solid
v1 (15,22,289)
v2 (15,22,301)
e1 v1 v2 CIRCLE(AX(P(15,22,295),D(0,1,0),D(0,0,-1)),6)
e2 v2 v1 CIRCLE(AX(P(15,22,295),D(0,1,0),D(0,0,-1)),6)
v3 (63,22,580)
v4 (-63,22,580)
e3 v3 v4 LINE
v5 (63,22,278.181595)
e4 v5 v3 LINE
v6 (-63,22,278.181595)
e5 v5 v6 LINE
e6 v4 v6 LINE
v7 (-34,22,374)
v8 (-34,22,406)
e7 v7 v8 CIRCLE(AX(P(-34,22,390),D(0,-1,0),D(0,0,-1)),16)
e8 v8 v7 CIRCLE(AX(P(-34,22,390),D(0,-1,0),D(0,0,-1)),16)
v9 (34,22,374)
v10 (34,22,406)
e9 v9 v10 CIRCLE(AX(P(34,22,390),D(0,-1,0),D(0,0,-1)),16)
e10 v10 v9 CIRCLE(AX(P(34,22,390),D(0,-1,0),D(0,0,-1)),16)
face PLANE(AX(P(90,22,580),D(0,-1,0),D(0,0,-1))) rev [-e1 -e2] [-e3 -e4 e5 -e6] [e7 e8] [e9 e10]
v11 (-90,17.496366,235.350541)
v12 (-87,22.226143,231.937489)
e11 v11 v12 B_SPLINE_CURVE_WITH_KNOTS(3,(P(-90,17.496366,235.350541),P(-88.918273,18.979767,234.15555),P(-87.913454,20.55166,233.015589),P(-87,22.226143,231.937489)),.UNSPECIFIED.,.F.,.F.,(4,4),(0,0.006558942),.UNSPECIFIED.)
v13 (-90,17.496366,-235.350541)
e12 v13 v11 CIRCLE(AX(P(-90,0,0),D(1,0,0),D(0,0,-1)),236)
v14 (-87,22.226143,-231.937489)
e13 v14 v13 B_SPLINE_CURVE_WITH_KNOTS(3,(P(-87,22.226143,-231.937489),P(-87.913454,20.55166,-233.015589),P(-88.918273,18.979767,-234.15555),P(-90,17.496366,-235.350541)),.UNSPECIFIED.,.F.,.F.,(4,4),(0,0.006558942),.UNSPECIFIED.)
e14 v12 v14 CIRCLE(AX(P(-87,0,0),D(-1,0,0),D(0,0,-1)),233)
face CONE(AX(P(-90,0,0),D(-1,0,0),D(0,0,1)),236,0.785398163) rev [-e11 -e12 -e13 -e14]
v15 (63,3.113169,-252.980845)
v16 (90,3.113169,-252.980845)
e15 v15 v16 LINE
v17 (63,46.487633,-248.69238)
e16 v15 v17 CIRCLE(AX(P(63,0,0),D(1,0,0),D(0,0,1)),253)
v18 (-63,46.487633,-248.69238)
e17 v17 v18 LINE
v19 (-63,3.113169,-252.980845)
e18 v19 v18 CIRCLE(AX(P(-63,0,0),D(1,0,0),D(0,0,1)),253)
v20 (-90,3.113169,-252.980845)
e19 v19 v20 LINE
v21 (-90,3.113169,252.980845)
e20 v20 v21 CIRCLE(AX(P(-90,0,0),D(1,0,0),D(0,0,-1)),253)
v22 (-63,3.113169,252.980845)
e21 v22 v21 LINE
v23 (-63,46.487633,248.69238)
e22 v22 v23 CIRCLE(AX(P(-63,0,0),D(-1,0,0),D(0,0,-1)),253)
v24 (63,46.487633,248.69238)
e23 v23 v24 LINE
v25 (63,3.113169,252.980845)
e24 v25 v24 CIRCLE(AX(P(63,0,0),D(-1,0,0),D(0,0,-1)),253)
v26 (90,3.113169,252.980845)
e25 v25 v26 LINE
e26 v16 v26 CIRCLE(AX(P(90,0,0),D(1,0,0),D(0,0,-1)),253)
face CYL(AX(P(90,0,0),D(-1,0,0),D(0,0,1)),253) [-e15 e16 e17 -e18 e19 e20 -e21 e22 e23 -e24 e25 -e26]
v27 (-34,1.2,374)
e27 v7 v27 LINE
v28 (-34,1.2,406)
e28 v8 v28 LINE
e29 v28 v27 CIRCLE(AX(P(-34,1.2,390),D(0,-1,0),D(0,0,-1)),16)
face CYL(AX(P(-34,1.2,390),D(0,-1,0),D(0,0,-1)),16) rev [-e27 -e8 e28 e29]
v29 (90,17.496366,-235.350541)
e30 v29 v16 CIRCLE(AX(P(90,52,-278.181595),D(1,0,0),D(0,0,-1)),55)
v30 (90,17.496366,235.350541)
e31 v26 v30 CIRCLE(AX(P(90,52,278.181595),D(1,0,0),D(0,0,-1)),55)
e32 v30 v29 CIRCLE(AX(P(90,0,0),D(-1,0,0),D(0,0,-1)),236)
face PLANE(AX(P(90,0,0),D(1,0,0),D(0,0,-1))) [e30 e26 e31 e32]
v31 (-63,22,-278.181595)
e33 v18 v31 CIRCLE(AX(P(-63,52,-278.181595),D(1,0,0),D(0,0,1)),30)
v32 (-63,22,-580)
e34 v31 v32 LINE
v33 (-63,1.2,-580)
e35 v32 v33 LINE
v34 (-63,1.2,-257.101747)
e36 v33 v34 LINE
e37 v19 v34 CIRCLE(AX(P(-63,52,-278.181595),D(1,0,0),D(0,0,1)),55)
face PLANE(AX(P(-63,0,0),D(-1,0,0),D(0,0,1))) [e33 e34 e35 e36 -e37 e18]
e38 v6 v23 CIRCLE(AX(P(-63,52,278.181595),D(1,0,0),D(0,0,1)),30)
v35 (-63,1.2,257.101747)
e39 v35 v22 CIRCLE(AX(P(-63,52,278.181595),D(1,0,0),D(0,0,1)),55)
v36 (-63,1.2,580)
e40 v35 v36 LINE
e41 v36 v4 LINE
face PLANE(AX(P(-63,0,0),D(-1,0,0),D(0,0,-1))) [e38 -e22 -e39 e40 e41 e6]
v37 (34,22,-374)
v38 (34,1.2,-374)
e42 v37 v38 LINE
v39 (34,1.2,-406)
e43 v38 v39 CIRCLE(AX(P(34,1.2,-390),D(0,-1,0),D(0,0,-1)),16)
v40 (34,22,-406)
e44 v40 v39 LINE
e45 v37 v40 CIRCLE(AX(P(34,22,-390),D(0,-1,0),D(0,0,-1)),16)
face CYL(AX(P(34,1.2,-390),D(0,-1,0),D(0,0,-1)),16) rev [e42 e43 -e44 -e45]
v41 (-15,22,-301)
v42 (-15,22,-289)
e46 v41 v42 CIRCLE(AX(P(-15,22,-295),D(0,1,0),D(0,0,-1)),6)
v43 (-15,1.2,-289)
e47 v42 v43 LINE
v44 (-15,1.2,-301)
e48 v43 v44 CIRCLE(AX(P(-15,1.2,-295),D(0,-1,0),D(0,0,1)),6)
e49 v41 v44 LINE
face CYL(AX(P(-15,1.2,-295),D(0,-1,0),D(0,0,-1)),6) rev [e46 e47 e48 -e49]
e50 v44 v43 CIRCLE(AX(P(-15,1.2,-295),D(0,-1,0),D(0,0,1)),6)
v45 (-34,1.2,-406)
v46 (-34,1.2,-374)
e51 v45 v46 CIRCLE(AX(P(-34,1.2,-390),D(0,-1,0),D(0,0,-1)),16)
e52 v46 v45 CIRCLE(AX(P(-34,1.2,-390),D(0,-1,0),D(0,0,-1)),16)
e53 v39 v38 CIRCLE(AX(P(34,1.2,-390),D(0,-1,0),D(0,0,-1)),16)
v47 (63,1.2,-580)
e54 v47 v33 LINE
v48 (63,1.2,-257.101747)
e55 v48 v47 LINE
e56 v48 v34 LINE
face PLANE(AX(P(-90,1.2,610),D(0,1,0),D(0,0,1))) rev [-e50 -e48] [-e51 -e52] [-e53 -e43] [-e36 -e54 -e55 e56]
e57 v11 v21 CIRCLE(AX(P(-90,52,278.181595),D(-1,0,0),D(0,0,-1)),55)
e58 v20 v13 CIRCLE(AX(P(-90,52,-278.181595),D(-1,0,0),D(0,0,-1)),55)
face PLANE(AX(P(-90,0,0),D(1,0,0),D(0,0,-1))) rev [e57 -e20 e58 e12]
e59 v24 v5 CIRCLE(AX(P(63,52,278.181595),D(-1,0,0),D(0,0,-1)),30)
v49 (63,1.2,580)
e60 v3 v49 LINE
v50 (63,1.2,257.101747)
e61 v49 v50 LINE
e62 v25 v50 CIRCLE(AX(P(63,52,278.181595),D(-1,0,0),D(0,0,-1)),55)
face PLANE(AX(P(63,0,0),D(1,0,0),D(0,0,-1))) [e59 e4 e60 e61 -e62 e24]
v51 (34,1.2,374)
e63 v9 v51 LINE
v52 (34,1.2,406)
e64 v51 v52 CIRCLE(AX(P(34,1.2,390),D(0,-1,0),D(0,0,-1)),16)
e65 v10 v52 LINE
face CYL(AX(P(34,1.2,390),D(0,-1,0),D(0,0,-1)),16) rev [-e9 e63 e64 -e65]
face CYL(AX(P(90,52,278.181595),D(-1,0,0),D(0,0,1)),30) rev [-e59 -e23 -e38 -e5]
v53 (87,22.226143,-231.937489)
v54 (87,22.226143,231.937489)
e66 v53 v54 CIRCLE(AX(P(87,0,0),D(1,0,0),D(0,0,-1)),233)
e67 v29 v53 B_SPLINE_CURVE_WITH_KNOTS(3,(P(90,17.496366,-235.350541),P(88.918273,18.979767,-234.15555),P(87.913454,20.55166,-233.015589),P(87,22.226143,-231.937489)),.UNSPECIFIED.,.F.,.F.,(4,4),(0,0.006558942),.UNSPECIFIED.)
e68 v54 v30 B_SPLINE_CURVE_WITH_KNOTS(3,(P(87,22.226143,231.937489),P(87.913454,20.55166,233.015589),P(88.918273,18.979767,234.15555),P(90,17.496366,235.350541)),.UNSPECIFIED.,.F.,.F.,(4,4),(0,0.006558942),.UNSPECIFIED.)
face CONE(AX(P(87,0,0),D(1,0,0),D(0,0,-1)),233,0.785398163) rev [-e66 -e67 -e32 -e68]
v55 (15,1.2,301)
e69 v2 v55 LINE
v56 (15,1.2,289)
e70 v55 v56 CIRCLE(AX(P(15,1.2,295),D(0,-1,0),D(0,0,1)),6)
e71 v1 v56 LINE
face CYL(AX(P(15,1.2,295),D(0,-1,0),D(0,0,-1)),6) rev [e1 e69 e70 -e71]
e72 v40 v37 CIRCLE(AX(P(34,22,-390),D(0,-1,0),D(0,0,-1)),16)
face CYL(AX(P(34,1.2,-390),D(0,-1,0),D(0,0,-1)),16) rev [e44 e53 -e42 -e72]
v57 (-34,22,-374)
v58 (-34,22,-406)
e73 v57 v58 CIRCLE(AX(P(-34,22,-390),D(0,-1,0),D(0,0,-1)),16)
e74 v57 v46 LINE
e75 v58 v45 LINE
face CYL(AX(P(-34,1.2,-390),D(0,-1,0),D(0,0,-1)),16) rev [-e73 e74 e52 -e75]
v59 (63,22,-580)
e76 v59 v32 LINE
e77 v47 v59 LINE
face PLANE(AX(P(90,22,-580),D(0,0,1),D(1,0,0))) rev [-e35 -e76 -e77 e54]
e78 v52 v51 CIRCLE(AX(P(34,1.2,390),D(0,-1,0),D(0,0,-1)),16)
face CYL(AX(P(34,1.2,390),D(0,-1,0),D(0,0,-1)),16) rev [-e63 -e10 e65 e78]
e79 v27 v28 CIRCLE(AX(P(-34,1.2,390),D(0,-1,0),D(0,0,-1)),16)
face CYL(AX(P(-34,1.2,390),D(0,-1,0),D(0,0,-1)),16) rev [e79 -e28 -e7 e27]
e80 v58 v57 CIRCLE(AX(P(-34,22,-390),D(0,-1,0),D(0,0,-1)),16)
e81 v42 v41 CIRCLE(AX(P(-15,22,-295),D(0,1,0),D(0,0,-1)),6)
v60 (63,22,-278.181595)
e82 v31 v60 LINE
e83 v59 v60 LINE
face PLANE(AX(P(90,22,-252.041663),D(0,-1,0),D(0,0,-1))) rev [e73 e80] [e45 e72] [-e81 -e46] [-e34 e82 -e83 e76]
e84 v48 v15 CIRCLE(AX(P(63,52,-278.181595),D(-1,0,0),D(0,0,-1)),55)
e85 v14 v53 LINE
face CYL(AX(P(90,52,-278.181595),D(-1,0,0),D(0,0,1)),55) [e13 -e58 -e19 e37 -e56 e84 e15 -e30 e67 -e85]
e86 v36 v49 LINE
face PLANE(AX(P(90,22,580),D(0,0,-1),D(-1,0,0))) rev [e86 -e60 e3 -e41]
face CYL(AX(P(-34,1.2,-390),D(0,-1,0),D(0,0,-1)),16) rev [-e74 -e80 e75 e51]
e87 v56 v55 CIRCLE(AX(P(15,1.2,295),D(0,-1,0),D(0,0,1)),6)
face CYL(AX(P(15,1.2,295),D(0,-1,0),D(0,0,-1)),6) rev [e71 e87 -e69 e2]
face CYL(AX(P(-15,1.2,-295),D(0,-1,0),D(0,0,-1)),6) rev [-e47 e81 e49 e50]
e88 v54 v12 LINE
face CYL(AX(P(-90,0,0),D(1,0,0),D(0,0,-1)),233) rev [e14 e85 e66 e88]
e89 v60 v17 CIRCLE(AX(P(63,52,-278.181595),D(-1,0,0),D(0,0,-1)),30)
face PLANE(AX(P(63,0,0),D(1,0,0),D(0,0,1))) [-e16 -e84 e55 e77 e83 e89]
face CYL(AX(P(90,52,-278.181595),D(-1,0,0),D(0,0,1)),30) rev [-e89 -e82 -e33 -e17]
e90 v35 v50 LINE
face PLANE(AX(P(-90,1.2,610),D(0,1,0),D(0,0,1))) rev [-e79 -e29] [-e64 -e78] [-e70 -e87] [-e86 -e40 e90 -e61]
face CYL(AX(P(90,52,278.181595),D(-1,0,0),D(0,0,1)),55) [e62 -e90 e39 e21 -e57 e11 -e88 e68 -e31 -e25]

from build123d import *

# Parameters (mm, degrees)
BOSS_EXTRUDE1_DEPTH     = 90
FILLET1_R               = 30
FILLET2_R               = 55
CUT_EXTRUDE1_START      = -90
SKETCH2_R               = 233
CUT_EXTRUDE1_DEPTH      = 180
CUT_EXTRUDE2_DEPTH      = 640.147087923
CUT_EXTRUDE2_DEPTH_BACK = 640.147087923
SKETCH3_W               = 1220
SKETCH3_H               = 21.2
CUT_EXTRUDE3_DEPTH      = 27
MIRROR2_COPY_1_DEPTH    = 27
CUT_EXTRUDE4_DEPTH      = 640.147087923
CUT_EXTRUDE4_DEPTH_BACK = 640.147087923
SKETCH5_R               = 15
SKETCH5_R_2             = 6
CHAMFER1_SIZE           = 3
M36_TAPPED_HOLE1_D      = 32


with BuildPart() as part:
    # Sketch1 → Boss-Extrude1 (new, symmetric)
    with BuildSketch(Plane(origin=(0, 0, 0), x_dir=(0, 0, -1), z_dir=(1, 0, 0))):
        with BuildLine():
            Line((-580, 22), (-252.041663223, 22))
            ThreePointArc((-252.041663223, 22), (0, 253), (252.041663223, 22))
            Line((252.041663223, 22), (580, 22))
            Line((580, 22), (580, -3))
            Line((580, -3), (227.980262304, -3))
            ThreePointArc((227.980262304, -3), (0, 228), (-227.980262304, -3))
            Line((-227.980262304, -3), (-580, -3))
            Line((-580, -3), (-580, 22))
        make_face()
    extrude(amount=BOSS_EXTRUDE1_DEPTH, both=True)

    # Fillet1
    fillet1_edges = [part.edges().sort_by_distance(p)[0] for p in [
        (0, 22, 252.041663223),
        (0, 22, -252.041663223),
    ]]
    fillet(fillet1_edges, radius=FILLET1_R)

    # Fillet2
    fillet2_edges = [part.edges().sort_by_distance(p)[0] for p in [
        (0, -3, -227.980262304),
        (0, -3, 227.980262304),
    ]]
    fillet(fillet2_edges, radius=FILLET2_R)

    # Sketch2 → Cut-Extrude1 (cut)
    with BuildSketch(Plane(origin=(0, 0, 0), x_dir=(0, 0, -1), z_dir=(1, 0, 0)).offset(CUT_EXTRUDE1_START)):
        Circle(SKETCH2_R)
    extrude(amount=CUT_EXTRUDE1_DEPTH, mode=Mode.SUBTRACT)

    # Sketch3 → Cut-Extrude2 (cut, two sides: drawn at the far end of the back side and taken through both)
    with BuildSketch(Plane(origin=(0, 0, 0), x_dir=(0, 0, -1), z_dir=(1, 0, 0)).offset(-CUT_EXTRUDE2_DEPTH_BACK)):
        with Locations((0, -9.4)):
            Rectangle(SKETCH3_W, SKETCH3_H)
    extrude(amount=CUT_EXTRUDE2_DEPTH + CUT_EXTRUDE2_DEPTH_BACK, mode=Mode.SUBTRACT)

    # Sketch4 → Cut-Extrude3 (cut)
    with BuildSketch(Plane(origin=(90, 0, 0), x_dir=(0, 0, -1), z_dir=(1, 0, 0))):
        with BuildLine():
            Line((-598.01008044, 50), (-248.01008044, 50))
            ThreePointArc((-248.01008044, 50), (-252.546221213, 15.14615962), (-252.208247288, -20))
            Line((-252.208247288, -20), (-598.01008044, -20))
            Line((-598.01008044, -20), (-598.01008044, 50))
        make_face()
    cut_extrude3 = extrude(amount=-CUT_EXTRUDE3_DEPTH, mode=Mode.SUBTRACT)

    # Mirror1: Cut-Extrude3 across plane
    add(cut_extrude3.mirror(Plane.XY), mode=Mode.SUBTRACT)

    # Mirror2: Cut-Extrude3 across plane
    add(cut_extrude3.mirror(Plane(origin=(0, 0, 0), x_dir=(0, 0, 1), z_dir=(1, 0, 0))), mode=Mode.SUBTRACT)

    # Mirror2 copy 1 sketch → Mirror2 copy 1 (cut)
    with BuildSketch(Plane.ZY.offset(90)):
        with BuildLine():
            Line((-598.01008044, 50), (-248.01008044, 50))
            ThreePointArc((-248.01008044, 50), (-252.546221213, 15.14615962), (-252.208247288, -20))
            Line((-252.208247288, -20), (-598.01008044, -20))
            Line((-598.01008044, -20), (-598.01008044, 50))
        make_face()
    extrude(amount=-MIRROR2_COPY_1_DEPTH, mode=Mode.SUBTRACT)

    # Sketch5 → Cut-Extrude4 (cut, two sides: drawn at the far end of the back side and taken through both)
    with BuildSketch(Plane(origin=(0, 0, 0), x_dir=(1, 0, 0), z_dir=(0, 1, 0)).offset(-CUT_EXTRUDE4_DEPTH_BACK)):
        with Locations(Location((34, -390, 0), (0, 0, 90))):
            Circle(SKETCH5_R)
        with Locations(Location((34, 390, 0), (0, 0, 90))):
            Circle(SKETCH5_R)
        with Locations(Location((-34, -390, 0), (0, 0, 90))):
            Circle(SKETCH5_R)
        with Locations(Location((-34, 390, 0), (0, 0, 90))):
            Circle(SKETCH5_R)
        with Locations(Location((15, -295, 0), (0, 0, 90))):
            Circle(SKETCH5_R_2)
        with Locations(Location((-15, 295, 0), (0, 0, 90))):
            Circle(SKETCH5_R_2)
    extrude(amount=CUT_EXTRUDE4_DEPTH + CUT_EXTRUDE4_DEPTH_BACK, mode=Mode.SUBTRACT)

    # Chamfer1
    chamfer1_edges = [part.edges().sort_by_distance(p)[0] for p in [
        (-90, 233, 0),
        (90, 233, 0),
    ]]
    chamfer(chamfer1_edges, length=CHAMFER1_SIZE)

    # M36 Tapped Hole1 (through all)
    with Locations(Plane(origin=(0, 1.2, 0), x_dir=(-1, 0, 0), z_dir=(0, -1, 0))):
        with Locations((34, -390), (-34, -390), (-34, 390), (34, 390)):
            Hole(M36_TAPPED_HOLE1_D / 2)


solid = part.part
